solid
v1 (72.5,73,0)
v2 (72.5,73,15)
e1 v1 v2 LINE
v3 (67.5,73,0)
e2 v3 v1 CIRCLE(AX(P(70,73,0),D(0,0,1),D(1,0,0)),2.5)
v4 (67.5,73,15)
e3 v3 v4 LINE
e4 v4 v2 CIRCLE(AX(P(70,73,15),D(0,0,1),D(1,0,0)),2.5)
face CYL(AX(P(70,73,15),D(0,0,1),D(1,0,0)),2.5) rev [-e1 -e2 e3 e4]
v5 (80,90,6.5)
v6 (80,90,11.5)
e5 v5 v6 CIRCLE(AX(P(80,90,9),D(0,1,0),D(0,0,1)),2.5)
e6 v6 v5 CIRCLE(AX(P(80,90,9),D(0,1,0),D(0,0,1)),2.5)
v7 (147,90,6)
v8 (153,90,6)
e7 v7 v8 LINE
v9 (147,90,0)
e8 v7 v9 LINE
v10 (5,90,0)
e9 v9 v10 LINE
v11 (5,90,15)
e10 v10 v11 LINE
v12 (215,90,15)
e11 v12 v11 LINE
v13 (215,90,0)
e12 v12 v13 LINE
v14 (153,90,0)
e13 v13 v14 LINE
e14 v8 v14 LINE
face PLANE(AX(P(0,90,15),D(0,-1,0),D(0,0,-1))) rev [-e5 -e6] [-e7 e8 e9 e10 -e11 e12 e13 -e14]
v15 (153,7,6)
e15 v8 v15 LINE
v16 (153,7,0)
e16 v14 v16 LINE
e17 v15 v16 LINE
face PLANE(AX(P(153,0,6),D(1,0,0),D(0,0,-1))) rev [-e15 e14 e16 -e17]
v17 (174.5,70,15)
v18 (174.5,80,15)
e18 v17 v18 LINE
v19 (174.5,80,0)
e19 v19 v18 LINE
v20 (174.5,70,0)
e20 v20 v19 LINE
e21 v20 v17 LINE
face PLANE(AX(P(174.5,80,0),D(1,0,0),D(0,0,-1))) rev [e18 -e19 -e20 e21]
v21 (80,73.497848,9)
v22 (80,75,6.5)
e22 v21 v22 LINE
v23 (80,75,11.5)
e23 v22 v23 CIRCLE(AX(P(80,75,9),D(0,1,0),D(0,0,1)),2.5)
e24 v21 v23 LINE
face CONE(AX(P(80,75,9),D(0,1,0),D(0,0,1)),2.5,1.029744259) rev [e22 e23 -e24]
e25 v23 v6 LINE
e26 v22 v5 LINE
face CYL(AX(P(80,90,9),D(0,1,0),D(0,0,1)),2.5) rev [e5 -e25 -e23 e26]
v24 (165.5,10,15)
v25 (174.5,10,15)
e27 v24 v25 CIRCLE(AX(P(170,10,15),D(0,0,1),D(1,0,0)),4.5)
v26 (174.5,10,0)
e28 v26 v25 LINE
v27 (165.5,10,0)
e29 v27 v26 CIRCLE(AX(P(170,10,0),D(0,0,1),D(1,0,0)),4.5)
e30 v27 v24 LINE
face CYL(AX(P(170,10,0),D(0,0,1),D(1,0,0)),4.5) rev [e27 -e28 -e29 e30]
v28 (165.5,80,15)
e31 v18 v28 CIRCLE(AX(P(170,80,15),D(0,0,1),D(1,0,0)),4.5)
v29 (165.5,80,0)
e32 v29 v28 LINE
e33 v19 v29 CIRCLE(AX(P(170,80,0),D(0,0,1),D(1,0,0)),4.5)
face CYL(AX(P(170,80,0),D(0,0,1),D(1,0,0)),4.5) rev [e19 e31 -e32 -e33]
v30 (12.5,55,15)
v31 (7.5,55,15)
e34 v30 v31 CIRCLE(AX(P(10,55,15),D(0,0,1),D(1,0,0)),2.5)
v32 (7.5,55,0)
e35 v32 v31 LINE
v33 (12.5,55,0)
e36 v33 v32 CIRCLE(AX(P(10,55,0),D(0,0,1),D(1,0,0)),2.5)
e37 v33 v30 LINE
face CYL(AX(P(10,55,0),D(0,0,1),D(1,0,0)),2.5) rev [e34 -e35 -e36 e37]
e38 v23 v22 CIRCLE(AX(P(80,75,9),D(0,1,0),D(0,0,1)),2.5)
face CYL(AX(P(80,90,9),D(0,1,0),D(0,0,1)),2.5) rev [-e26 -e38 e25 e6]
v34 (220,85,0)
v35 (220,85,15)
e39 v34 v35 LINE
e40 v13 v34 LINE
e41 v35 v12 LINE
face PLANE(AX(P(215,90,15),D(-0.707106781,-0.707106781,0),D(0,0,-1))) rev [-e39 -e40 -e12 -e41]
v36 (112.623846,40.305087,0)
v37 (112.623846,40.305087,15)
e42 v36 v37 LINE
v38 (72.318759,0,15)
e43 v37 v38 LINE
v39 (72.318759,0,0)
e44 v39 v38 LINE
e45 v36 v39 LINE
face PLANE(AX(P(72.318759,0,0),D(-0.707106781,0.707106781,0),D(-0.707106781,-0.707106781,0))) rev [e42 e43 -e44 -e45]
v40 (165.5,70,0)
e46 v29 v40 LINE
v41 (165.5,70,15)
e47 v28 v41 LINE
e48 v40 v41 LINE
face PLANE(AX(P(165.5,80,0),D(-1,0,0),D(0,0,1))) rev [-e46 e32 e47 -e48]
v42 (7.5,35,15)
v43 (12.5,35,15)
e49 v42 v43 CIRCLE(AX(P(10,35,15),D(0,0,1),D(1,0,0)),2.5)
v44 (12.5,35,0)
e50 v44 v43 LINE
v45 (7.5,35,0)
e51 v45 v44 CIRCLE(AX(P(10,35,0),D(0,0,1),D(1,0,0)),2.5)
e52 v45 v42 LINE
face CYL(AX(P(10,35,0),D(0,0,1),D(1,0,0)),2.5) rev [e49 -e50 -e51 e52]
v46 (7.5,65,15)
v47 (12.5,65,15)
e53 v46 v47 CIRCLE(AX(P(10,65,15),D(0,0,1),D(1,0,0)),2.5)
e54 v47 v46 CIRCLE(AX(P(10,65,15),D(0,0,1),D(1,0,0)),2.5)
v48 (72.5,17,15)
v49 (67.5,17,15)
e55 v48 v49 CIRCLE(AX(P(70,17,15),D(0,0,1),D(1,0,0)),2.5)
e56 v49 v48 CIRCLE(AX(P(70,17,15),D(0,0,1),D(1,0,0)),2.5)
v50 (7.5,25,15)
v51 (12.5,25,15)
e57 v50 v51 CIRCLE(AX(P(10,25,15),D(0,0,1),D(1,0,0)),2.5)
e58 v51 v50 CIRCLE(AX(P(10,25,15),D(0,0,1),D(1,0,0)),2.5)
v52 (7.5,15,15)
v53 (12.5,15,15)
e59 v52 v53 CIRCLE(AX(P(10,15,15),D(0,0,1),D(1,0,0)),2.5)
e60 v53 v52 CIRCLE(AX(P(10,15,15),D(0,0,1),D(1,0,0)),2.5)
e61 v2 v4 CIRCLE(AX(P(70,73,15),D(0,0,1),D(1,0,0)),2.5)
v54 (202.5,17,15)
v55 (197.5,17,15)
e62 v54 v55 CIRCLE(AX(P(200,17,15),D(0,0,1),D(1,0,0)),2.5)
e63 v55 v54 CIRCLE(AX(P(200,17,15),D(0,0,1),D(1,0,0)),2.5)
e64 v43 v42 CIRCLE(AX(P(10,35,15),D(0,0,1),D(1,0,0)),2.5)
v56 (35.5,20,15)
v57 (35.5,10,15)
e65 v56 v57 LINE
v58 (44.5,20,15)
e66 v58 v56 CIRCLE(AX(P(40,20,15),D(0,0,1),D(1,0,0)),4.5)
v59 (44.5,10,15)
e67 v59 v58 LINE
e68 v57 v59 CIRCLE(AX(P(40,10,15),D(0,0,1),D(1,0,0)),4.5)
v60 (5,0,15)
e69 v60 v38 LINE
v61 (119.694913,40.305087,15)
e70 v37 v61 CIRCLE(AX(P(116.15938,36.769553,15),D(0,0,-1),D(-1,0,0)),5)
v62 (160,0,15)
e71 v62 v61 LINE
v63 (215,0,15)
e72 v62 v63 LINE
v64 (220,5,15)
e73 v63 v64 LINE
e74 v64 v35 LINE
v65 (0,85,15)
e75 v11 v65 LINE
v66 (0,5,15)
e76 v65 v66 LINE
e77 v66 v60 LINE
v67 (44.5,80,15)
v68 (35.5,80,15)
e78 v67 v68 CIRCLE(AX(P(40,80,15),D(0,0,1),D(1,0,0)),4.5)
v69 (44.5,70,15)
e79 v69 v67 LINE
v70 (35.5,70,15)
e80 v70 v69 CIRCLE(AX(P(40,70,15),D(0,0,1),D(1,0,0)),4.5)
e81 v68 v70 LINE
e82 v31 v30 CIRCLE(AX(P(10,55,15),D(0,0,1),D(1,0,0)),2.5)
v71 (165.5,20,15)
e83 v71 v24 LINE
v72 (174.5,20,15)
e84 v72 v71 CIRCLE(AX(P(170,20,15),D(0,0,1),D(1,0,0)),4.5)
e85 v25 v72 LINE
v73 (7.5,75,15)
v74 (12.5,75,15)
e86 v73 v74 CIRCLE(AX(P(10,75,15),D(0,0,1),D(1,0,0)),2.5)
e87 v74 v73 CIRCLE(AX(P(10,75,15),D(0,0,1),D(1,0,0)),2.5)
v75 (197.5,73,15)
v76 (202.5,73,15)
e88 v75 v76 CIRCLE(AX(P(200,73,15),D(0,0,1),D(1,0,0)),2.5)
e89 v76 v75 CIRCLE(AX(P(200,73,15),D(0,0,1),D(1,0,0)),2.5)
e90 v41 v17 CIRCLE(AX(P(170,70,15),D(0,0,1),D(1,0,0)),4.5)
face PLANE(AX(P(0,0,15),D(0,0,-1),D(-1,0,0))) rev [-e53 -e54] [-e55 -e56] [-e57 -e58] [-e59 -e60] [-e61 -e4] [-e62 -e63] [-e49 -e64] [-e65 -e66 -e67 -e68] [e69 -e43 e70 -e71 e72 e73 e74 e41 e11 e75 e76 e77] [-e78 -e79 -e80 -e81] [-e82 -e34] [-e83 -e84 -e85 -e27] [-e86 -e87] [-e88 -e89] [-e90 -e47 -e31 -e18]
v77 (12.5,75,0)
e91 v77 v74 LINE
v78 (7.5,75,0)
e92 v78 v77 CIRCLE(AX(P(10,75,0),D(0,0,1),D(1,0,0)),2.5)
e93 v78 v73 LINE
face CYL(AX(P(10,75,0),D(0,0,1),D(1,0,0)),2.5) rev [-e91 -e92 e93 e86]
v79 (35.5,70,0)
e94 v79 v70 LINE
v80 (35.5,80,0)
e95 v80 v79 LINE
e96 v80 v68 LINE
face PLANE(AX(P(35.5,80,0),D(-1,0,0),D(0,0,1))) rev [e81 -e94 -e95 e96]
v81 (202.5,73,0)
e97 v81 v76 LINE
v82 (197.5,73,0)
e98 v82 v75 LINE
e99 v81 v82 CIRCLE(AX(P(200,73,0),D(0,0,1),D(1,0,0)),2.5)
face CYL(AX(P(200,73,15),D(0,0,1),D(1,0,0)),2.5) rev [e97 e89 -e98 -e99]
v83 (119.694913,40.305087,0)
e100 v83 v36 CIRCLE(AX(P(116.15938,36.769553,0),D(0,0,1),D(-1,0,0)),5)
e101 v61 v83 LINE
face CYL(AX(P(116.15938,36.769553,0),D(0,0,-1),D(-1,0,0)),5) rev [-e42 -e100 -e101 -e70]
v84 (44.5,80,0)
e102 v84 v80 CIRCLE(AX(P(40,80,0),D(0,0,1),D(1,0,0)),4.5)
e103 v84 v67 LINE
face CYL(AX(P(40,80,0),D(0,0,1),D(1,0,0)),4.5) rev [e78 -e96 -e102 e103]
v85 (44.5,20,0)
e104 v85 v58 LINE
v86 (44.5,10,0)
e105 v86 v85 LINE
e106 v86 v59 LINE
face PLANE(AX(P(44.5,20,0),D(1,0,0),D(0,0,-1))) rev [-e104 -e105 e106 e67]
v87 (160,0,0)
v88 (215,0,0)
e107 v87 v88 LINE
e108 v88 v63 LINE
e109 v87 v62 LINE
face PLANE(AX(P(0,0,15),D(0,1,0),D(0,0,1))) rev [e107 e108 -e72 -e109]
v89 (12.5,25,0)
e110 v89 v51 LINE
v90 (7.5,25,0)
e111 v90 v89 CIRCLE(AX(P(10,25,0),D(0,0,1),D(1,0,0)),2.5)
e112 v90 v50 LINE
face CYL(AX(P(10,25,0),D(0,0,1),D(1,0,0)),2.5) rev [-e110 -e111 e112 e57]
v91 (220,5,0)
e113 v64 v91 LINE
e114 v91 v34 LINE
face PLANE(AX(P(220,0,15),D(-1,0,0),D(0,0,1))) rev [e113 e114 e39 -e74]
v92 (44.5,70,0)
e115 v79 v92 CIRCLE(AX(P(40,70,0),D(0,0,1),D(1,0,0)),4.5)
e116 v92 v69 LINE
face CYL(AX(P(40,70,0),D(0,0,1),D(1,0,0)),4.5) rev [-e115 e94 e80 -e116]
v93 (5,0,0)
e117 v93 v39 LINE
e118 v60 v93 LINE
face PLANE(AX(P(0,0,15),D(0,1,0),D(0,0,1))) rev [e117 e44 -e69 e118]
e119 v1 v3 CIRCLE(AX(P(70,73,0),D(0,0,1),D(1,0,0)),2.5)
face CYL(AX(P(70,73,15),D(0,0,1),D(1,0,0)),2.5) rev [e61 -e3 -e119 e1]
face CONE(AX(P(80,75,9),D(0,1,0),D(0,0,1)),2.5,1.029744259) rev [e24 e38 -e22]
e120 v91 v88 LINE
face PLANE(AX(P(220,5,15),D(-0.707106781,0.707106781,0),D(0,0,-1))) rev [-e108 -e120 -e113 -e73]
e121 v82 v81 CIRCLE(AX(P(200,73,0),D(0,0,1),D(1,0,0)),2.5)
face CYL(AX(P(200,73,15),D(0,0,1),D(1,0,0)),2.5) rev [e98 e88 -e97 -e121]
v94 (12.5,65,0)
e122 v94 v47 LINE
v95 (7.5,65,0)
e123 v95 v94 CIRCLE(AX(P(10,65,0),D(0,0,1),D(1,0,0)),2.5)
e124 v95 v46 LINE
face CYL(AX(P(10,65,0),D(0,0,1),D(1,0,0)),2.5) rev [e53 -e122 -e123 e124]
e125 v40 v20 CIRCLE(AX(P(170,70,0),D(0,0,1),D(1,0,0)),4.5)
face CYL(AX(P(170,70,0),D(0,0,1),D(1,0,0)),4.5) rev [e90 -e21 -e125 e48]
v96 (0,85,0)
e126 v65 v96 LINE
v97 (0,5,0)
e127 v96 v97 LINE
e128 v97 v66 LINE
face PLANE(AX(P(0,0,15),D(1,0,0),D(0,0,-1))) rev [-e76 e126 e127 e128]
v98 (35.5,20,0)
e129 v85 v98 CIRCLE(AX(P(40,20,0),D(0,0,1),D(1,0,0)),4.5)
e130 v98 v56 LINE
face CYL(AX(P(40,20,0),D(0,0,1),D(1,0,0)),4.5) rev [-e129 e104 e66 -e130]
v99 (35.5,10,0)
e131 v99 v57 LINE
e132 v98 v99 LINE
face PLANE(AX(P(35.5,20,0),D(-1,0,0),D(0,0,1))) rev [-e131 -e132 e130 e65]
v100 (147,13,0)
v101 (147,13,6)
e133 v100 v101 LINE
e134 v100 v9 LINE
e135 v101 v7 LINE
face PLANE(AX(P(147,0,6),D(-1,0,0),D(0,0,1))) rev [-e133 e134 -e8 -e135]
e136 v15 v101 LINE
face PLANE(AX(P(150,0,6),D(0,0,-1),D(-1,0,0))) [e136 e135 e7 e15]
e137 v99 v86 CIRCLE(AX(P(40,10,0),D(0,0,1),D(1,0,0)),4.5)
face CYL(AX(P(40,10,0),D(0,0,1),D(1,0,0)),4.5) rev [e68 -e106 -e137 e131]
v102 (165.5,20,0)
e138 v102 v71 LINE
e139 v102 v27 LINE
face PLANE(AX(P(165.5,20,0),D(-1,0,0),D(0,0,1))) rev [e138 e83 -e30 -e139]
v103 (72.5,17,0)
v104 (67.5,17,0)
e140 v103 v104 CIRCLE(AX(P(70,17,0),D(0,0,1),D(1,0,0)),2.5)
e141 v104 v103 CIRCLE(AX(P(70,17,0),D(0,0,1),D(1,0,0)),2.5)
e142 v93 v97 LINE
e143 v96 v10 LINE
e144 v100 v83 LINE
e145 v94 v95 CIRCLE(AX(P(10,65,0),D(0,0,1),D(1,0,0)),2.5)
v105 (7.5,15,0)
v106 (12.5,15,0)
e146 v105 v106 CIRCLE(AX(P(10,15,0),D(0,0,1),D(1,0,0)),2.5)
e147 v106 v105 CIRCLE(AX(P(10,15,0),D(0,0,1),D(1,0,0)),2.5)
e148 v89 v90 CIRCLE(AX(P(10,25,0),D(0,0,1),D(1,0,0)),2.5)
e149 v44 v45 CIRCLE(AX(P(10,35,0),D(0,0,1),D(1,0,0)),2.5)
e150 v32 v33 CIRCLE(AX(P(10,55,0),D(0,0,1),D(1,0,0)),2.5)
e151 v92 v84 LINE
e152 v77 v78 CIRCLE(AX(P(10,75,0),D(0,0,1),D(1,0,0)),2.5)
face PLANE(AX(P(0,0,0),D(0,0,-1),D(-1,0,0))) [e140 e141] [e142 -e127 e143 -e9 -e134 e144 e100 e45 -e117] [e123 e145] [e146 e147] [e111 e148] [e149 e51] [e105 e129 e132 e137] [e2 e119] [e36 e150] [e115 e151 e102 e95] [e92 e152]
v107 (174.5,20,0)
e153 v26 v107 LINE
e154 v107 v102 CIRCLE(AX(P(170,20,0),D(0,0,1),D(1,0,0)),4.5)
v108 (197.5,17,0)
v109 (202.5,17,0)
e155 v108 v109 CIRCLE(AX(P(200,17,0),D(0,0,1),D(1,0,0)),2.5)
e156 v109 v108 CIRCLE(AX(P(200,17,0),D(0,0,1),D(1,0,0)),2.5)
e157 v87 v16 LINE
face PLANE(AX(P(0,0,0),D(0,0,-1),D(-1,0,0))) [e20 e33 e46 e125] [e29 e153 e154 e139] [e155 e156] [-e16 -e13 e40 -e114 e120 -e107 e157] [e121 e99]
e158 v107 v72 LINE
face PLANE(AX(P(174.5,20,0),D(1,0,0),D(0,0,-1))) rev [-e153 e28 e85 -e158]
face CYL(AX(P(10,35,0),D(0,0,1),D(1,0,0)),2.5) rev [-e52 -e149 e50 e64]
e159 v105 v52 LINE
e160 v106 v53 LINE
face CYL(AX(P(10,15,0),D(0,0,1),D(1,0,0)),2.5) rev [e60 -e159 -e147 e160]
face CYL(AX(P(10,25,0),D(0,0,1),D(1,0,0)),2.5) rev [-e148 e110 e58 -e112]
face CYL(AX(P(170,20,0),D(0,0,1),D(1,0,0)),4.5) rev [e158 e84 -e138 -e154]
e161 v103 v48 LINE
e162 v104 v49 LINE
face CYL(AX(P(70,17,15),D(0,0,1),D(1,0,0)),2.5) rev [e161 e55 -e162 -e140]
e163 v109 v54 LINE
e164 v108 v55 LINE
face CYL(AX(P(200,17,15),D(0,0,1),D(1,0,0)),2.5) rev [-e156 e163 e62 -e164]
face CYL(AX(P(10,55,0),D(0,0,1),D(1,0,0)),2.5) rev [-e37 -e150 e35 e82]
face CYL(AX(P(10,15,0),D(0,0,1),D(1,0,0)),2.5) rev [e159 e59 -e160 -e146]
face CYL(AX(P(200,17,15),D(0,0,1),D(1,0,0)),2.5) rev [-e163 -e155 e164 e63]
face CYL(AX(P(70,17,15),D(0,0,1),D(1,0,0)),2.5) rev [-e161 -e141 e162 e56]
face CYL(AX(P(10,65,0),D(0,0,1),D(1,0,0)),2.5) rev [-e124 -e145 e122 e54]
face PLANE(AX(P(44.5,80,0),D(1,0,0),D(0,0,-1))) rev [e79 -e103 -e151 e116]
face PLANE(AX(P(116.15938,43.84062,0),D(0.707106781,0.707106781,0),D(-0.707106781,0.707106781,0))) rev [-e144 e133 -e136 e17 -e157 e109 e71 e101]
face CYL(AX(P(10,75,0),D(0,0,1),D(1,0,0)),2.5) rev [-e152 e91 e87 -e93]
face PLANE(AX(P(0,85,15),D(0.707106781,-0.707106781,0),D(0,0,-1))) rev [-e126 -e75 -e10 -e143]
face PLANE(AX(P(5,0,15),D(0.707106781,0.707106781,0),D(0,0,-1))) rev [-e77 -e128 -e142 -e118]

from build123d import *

# Parameters (mm, degrees)
SKETCH1_W             = 220
SKETCH1_H             = 90
BOSS_EXTRUDE1_DEPTH   = 15
M6_TAPPED_HOLE1_D     = 5
M6_TAPPED_HOLE1_DEPTH = 15
M6_TAPPED_HOLE1_TIP   = 1.502151548
CUT_EXTRUDE1_DEPTH    = 239.170107276
CUT_EXTRUDE2_DEPTH    = 239.170107276
M6_TAPPED_HOLE2_D     = 5
M6_TAPPED_HOLE2_DEPTH = 15
M6_TAPPED_HOLE2_TIP   = 1.502151548
CHAMFER1_SIZE         = 5
FILLET1_R             = 5
CUT_EXTRUDE3_DEPTH    = 6
SKETCH11_R            = 2.5
CUT_EXTRUDE4_DEPTH    = 239.170107276


with BuildPart() as part:
    # Sketch1 → Boss-Extrude1 (new body)
    with BuildSketch(Plane.XY):
        with Locations((110, 45)):
            Rectangle(SKETCH1_W, SKETCH1_H)
    extrude(amount=BOSS_EXTRUDE1_DEPTH)

    # M6 Tapped Hole1
    with Locations(Plane.XY.offset(15)):
        with Locations((70, 73), (70, 17), (200, 73), (200, 17)):
            Hole(M6_TAPPED_HOLE1_D / 2, depth=M6_TAPPED_HOLE1_DEPTH)
            with Locations((0, 0, -(M6_TAPPED_HOLE1_DEPTH + M6_TAPPED_HOLE1_TIP / 2))):  # 118° drill point
                Cone(0, M6_TAPPED_HOLE1_D / 2, M6_TAPPED_HOLE1_TIP, mode=Mode.SUBTRACT)

    # Sketch4 → Cut-Extrude1 (cut, through all)
    with BuildSketch(Plane.XY.offset(15)):
        with BuildLine():
            Line((44.5, 80), (44.5, 70))
            ThreePointArc((44.5, 70), (40, 65.5), (35.5, 70))
            Line((35.5, 70), (35.5, 80))
            ThreePointArc((35.5, 80), (40, 84.5), (44.5, 80))
        make_face()
        with BuildLine():
            Line((44.5, 20), (44.5, 10))
            ThreePointArc((44.5, 10), (40, 5.5), (35.5, 10))
            Line((35.5, 10), (35.5, 20))
            ThreePointArc((35.5, 20), (40, 24.5), (44.5, 20))
        make_face()
        with BuildLine():
            Line((174.5, 80), (174.5, 70))
            ThreePointArc((174.5, 70), (170, 65.5), (165.5, 70))
            Line((165.5, 70), (165.5, 80))
            ThreePointArc((165.5, 80), (170, 84.5), (174.5, 80))
        make_face()
        with BuildLine():
            Line((174.5, 20), (174.5, 10))
            ThreePointArc((174.5, 10), (170, 5.5), (165.5, 10))
            Line((165.5, 10), (165.5, 20))
            ThreePointArc((165.5, 20), (170, 24.5), (174.5, 20))
        make_face()
    extrude(amount=-CUT_EXTRUDE1_DEPTH, mode=Mode.SUBTRACT)

    # Sketch5 → Cut-Extrude2 (cut, through all)
    with BuildSketch(Plane.XY.offset(15)):
        Polygon((72.318759133, 0), (116.159379566, 43.840620434), (160, 0), (116.159379566, -43.840620434), align=None)
    extrude(amount=-CUT_EXTRUDE2_DEPTH, mode=Mode.SUBTRACT)

    # M6 Tapped Hole2
    with Locations(Plane(origin=(0, 90, 0), x_dir=(1, 0, 0), z_dir=(0, 1, 0))):
        with Locations((80, -9)):
            Hole(M6_TAPPED_HOLE2_D / 2, depth=M6_TAPPED_HOLE2_DEPTH)
            with Locations((0, 0, -(M6_TAPPED_HOLE2_DEPTH + M6_TAPPED_HOLE2_TIP / 2))):  # 118° drill point
                Cone(0, M6_TAPPED_HOLE2_D / 2, M6_TAPPED_HOLE2_TIP, mode=Mode.SUBTRACT)

    # Chamfer1
    chamfer1_edges = [part.edges().sort_by_distance(p)[0] for p in [
        (0, 90, 7.5),
        (220, 90, 7.5),
        (220, 0, 7.5),
        (0, 0, 7.5),
    ]]
    chamfer(chamfer1_edges, length=CHAMFER1_SIZE)

    # Fillet1
    fillet1_edges = [part.edges().sort_by_distance(p)[0] for p in [
        (116.159379566, 43.840620434, 7.5),
    ]]
    fillet(fillet1_edges, radius=FILLET1_R)

    # Sketch10 → Cut-Extrude3 (cut)
    with BuildSketch(Plane(origin=(0, 0, 0), x_dir=(-1, 0, 0), z_dir=(0, 0, -1))):
        with BuildLine():
            Line((-153, 0), (-153, 90))
            ThreePointArc((-153, 90), (-150, 93), (-147, 90))
            Line((-147, 90), (-147, 0))
            ThreePointArc((-147, 0), (-150, -3), (-153, 0))
        make_face()
    extrude(amount=-CUT_EXTRUDE3_DEPTH, mode=Mode.SUBTRACT)

    # Sketch11 → Cut-Extrude4 (cut, through all)
    with BuildSketch(Plane.XY.offset(15)):
        with Locations((10, 55)):
            Circle(SKETCH11_R)
        with Locations((10, 35)):
            Circle(SKETCH11_R)
        with Locations((10, 25)):
            Circle(SKETCH11_R)
        with Locations((10, 65)):
            Circle(SKETCH11_R)
        with Locations((10, 75)):
            Circle(SKETCH11_R)
        with Locations((10, 15)):
            Circle(SKETCH11_R)
    extrude(amount=-CUT_EXTRUDE4_DEPTH, mode=Mode.SUBTRACT)


solid = part.part
